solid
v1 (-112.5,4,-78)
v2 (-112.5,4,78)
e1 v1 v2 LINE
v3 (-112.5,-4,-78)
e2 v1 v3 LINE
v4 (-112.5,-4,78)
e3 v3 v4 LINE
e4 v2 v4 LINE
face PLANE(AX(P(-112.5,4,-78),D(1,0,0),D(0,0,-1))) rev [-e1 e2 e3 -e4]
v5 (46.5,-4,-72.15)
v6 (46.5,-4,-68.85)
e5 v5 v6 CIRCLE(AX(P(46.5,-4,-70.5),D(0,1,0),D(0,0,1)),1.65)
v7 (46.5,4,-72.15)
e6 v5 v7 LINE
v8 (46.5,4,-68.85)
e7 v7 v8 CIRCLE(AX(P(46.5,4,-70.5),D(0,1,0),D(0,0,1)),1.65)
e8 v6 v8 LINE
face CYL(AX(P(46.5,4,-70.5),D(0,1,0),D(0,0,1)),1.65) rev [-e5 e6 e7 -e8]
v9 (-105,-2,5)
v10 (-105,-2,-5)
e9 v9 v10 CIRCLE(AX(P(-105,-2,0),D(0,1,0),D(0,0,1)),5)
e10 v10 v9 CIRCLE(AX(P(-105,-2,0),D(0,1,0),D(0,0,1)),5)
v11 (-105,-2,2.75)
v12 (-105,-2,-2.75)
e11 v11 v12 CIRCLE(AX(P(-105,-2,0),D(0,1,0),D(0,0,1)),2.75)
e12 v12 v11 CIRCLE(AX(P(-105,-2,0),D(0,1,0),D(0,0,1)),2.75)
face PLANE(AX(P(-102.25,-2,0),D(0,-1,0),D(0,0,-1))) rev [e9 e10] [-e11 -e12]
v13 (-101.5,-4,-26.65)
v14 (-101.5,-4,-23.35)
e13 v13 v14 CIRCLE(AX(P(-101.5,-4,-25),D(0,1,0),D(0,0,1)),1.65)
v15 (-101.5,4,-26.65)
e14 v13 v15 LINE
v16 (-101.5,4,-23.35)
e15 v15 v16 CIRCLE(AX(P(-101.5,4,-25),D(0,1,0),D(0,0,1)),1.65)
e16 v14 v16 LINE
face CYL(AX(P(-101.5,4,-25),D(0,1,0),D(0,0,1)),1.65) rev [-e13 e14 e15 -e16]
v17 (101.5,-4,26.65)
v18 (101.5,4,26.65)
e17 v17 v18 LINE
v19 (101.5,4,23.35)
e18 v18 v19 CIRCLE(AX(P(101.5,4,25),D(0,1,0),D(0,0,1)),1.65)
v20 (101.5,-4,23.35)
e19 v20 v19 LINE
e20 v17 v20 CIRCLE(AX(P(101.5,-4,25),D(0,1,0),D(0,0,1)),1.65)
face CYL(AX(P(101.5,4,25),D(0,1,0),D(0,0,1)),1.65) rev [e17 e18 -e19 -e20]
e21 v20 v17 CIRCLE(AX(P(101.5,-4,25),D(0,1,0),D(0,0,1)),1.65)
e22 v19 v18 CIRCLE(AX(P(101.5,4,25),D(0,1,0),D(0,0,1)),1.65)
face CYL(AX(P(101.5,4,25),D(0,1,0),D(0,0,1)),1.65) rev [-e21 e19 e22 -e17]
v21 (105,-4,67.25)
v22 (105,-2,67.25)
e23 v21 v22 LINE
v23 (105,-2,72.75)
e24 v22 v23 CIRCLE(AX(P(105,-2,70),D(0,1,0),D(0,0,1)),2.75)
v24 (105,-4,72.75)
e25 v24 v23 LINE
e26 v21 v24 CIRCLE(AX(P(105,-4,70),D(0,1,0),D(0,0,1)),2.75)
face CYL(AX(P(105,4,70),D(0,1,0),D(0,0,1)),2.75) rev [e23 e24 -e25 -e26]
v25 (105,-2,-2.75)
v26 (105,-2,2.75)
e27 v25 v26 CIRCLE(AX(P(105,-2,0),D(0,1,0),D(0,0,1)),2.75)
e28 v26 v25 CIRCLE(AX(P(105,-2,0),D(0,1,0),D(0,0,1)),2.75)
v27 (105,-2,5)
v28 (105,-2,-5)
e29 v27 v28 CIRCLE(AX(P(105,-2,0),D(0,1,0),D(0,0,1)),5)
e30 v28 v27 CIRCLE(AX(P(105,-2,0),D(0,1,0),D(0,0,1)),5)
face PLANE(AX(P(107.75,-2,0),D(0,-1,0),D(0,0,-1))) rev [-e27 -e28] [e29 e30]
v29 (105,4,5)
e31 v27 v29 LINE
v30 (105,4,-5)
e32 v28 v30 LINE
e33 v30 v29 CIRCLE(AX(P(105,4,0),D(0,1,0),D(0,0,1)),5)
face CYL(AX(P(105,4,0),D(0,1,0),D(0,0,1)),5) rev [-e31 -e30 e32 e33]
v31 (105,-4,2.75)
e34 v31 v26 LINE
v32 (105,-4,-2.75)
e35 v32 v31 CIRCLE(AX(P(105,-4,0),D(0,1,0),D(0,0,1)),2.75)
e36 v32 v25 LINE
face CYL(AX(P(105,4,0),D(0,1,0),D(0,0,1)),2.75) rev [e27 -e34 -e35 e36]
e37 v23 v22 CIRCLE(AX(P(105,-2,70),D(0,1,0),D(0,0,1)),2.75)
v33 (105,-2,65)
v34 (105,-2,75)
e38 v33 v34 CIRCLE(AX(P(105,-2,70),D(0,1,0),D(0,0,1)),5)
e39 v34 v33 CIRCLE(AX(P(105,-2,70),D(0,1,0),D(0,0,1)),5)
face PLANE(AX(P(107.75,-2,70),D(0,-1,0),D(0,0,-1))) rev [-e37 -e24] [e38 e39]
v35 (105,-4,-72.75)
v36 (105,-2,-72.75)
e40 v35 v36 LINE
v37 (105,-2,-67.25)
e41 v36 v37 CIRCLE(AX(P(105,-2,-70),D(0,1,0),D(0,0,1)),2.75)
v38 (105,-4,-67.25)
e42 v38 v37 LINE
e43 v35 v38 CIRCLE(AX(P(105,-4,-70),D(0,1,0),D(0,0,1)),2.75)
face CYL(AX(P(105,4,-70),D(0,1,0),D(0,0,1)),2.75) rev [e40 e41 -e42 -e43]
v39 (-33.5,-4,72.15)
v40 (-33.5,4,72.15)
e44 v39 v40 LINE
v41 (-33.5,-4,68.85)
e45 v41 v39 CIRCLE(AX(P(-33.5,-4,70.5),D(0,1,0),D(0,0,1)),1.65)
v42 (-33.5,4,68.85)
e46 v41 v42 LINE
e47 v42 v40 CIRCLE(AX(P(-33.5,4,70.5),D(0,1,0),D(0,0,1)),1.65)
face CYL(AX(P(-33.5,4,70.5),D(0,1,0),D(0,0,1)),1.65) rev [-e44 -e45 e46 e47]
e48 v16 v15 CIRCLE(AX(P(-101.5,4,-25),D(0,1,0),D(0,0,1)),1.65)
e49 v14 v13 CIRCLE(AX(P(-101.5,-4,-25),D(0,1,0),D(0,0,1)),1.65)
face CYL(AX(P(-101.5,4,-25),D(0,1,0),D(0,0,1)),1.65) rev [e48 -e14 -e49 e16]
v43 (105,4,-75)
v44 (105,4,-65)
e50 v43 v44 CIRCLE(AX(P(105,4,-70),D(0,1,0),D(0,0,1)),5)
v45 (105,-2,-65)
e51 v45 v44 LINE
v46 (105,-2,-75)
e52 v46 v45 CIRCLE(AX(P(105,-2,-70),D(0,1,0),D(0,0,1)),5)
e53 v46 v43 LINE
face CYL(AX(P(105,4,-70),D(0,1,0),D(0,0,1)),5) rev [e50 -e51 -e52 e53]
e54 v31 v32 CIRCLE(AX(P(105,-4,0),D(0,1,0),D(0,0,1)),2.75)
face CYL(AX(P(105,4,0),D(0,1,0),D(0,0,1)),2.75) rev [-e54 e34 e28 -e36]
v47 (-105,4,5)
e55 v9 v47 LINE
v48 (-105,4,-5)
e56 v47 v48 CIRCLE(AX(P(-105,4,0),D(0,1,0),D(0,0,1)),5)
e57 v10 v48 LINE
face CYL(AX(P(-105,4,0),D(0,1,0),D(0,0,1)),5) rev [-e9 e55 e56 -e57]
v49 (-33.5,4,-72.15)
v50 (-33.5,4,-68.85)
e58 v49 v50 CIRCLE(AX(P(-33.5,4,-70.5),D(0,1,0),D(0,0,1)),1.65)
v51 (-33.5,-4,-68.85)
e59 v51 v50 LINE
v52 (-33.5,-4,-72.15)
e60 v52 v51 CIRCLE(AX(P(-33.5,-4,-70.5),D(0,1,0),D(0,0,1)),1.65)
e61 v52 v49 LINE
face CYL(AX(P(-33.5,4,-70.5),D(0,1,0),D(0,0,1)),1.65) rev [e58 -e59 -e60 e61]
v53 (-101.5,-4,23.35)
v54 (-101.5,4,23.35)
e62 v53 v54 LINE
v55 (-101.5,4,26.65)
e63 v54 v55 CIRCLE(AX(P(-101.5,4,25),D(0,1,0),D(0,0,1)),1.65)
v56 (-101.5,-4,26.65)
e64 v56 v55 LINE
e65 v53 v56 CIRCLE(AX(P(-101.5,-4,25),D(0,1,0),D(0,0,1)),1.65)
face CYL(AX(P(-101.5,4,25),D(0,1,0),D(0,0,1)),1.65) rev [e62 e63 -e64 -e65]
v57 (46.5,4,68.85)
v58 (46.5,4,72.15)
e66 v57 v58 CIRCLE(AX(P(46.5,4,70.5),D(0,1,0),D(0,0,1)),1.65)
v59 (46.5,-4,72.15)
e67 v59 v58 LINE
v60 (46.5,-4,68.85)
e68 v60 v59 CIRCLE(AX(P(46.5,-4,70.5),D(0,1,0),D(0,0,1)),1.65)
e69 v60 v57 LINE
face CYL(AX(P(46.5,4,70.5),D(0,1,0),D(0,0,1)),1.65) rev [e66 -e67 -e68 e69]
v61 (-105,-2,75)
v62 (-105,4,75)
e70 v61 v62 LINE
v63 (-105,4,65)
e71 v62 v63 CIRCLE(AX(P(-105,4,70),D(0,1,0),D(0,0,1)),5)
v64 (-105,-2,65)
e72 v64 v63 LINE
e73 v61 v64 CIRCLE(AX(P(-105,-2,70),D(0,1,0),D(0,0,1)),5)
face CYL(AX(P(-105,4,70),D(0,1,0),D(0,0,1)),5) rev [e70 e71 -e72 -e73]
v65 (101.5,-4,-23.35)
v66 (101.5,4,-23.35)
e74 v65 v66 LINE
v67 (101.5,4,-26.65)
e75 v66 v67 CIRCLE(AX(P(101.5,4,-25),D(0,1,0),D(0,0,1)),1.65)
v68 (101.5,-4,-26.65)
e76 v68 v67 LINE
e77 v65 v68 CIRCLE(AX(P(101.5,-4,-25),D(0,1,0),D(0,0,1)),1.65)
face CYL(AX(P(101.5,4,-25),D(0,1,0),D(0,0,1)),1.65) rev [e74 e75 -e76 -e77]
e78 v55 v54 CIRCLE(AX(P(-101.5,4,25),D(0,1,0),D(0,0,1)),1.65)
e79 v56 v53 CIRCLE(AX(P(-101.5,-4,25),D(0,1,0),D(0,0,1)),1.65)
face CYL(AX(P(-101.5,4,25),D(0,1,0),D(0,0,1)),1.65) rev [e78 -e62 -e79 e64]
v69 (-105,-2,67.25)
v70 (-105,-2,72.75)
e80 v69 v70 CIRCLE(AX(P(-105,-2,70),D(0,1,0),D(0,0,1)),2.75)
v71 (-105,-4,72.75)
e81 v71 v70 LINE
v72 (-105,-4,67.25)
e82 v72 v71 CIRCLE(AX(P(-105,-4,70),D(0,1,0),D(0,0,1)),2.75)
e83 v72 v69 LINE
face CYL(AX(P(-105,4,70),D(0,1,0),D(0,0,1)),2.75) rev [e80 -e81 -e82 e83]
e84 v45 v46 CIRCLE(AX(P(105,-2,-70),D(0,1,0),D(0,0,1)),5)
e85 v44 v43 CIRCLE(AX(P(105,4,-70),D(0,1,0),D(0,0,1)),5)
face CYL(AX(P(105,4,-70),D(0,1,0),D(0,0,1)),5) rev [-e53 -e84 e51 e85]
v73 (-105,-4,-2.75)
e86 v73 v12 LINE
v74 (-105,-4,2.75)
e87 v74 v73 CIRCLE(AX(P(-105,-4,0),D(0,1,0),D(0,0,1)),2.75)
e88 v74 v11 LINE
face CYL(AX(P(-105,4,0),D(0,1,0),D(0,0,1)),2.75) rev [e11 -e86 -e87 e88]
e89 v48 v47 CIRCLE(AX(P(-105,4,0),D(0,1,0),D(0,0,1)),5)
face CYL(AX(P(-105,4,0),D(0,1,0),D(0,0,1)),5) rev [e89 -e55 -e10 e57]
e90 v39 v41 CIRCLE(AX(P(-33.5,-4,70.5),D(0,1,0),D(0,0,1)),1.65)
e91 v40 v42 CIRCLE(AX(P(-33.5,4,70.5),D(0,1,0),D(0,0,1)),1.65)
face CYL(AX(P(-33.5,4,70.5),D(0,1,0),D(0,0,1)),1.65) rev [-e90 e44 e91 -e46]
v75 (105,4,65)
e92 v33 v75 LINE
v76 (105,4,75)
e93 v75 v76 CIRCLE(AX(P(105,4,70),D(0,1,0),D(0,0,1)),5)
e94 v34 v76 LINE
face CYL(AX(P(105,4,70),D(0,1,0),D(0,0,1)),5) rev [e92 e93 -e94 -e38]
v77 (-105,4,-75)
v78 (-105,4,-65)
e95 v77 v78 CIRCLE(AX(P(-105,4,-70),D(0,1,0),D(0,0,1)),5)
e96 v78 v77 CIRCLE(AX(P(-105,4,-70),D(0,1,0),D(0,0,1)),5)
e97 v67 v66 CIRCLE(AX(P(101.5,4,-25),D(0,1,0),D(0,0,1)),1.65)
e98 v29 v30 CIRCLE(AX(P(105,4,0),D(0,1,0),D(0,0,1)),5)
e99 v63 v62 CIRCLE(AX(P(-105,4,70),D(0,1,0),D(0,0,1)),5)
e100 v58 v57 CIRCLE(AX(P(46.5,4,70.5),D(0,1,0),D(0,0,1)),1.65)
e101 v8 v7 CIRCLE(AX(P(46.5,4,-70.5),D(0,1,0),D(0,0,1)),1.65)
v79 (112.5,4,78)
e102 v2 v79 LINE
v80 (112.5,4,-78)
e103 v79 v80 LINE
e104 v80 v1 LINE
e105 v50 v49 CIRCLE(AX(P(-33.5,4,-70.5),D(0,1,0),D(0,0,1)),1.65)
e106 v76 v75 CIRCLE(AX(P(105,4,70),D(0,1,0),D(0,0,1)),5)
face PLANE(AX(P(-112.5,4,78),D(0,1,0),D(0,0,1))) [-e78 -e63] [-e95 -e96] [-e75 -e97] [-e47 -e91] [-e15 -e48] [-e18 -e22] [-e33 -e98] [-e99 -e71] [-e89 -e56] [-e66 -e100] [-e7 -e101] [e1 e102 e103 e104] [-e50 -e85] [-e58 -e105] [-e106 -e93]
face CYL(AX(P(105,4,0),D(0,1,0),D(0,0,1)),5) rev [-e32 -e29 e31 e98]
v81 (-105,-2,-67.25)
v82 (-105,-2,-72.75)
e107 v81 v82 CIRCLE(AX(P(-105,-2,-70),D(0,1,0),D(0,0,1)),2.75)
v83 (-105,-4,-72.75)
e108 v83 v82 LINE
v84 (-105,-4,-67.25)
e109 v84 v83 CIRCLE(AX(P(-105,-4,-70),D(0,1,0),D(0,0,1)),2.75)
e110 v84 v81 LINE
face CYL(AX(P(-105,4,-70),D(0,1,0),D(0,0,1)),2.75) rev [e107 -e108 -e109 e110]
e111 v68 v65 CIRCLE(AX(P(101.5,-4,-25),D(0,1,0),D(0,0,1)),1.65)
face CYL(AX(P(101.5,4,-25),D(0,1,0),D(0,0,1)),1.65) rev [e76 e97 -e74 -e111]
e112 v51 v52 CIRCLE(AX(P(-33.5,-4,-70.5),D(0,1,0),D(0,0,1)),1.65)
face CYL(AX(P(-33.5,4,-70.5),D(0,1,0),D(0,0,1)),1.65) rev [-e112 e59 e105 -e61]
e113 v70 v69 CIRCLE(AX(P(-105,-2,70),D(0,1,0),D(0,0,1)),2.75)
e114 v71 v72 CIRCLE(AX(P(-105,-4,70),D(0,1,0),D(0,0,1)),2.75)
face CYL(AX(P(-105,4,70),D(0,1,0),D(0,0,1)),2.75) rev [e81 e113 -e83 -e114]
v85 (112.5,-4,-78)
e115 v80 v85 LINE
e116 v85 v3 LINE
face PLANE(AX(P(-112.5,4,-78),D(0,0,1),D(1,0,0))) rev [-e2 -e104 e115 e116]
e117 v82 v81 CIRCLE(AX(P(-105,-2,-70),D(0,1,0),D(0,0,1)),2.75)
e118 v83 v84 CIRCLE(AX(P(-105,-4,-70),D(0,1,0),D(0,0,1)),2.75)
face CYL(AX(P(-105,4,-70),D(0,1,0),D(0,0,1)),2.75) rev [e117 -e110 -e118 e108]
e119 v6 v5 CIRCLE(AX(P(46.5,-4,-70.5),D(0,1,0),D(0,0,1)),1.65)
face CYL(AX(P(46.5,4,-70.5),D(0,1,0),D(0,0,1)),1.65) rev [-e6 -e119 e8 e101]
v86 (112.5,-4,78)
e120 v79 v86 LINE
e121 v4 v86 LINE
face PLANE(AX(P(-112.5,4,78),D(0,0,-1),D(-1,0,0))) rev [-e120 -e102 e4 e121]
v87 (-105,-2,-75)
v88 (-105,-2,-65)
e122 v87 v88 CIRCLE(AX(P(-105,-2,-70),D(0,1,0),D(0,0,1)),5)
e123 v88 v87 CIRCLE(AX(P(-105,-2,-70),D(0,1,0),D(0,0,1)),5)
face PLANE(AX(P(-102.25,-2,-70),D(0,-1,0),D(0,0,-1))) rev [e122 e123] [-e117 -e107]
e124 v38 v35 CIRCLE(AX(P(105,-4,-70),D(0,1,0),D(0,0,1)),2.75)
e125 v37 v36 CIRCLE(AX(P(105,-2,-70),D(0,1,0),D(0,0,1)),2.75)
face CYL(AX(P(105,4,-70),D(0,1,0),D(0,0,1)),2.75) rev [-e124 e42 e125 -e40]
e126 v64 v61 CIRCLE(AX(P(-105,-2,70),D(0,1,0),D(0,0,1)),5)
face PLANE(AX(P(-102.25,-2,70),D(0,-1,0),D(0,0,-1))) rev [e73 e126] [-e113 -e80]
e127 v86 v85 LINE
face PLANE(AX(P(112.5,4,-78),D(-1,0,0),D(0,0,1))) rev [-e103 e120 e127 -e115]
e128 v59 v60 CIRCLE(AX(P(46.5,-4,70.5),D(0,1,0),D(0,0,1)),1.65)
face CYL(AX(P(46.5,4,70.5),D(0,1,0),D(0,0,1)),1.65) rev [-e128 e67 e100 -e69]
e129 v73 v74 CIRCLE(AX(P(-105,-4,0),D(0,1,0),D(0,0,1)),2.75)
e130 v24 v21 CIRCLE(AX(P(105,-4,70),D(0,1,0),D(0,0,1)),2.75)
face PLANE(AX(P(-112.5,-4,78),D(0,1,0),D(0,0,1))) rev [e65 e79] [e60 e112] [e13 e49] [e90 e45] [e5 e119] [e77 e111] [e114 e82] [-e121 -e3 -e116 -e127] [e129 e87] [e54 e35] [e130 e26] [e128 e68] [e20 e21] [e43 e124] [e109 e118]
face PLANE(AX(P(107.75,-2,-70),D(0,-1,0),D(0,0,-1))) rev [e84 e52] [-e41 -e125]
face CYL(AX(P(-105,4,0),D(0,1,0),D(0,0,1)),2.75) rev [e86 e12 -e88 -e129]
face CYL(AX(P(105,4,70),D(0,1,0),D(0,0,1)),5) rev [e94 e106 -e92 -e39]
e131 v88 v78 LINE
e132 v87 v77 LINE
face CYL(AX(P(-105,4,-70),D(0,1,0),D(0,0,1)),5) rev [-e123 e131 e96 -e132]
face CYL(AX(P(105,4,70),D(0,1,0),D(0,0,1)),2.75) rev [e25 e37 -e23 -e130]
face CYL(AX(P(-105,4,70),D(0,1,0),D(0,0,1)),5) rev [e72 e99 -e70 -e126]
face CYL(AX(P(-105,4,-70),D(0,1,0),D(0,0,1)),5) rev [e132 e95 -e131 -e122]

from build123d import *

# Parameters (mm, degrees)
SKETCH1_W                                         = 225
SKETCH1_H                                         = 156
EXTRUDE1_DEPTH                                    = 4
M5_SOCKET_HEAD_CAP_SCREW_COUNTERBORE1_D           = 5.5
M5_SOCKET_HEAD_CAP_SCREW_COUNTERBORE1_CBORE_D     = 10
M5_SOCKET_HEAD_CAP_SCREW_COUNTERBORE1_CBORE_DEPTH = 6
M4_TAPPED_HOLE1_D                                 = 3.3
M4_TAPPED_HOLE2_D                                 = 3.3


with BuildPart() as part:
    # Sketch1 → Extrude1 (new, symmetric)
    with BuildSketch(Plane(origin=(0, 0, 0), x_dir=(1, 0, 0), z_dir=(0, 1, 0))):
        Rectangle(SKETCH1_W, SKETCH1_H)
    extrude(amount=EXTRUDE1_DEPTH, both=True)

    # M5 Socket Head Cap Screw Counterbore1 (through all)
    with Locations(Plane(origin=(105, 4, 70), x_dir=(0, 0, 1), z_dir=(0, 1, 0))):
        with Locations((0, 0), (-70, 0), (-140, 0)):
            m5_socket_head_cap_screw_counterbore1 = CounterBoreHole(M5_SOCKET_HEAD_CAP_SCREW_COUNTERBORE1_D / 2, M5_SOCKET_HEAD_CAP_SCREW_COUNTERBORE1_CBORE_D / 2, M5_SOCKET_HEAD_CAP_SCREW_COUNTERBORE1_CBORE_DEPTH)

    # Mirror1: M5 Socket Head Cap Screw Counterbore1 across plane
    add(m5_socket_head_cap_screw_counterbore1.mirror(Plane(origin=(0, 0, 0), x_dir=(0, 0, 1), z_dir=(1, 0, 0))), mode=Mode.SUBTRACT)

    # M4 Tapped Hole1 (through all)
    with Locations(Plane(origin=(101.5, 4, 25), x_dir=(0, 0, 1), z_dir=(0, 1, 0))):
        with Locations((0, 0), (-50, 0)):
            m4_tapped_hole1 = Hole(M4_TAPPED_HOLE1_D / 2)

    # M4 Tapped Hole2 (through all)
    with Locations(Plane(origin=(-33.5, 4, 70.5), x_dir=(0, 0, 1), z_dir=(0, 1, 0))):
        with Locations((0, 0), (0, 80)):
            m4_tapped_hole2 = Hole(M4_TAPPED_HOLE2_D / 2)

    # Mirror2: M4 Tapped Hole1 across plane
    add(m4_tapped_hole1.mirror(Plane(origin=(0, 0, 0), x_dir=(0, 0, 1), z_dir=(1, 0, 0))), mode=Mode.SUBTRACT)

    # Mirror3: M4 Tapped Hole2 across plane
    add(m4_tapped_hole2.mirror(Plane.XY), mode=Mode.SUBTRACT)


solid = part.part
